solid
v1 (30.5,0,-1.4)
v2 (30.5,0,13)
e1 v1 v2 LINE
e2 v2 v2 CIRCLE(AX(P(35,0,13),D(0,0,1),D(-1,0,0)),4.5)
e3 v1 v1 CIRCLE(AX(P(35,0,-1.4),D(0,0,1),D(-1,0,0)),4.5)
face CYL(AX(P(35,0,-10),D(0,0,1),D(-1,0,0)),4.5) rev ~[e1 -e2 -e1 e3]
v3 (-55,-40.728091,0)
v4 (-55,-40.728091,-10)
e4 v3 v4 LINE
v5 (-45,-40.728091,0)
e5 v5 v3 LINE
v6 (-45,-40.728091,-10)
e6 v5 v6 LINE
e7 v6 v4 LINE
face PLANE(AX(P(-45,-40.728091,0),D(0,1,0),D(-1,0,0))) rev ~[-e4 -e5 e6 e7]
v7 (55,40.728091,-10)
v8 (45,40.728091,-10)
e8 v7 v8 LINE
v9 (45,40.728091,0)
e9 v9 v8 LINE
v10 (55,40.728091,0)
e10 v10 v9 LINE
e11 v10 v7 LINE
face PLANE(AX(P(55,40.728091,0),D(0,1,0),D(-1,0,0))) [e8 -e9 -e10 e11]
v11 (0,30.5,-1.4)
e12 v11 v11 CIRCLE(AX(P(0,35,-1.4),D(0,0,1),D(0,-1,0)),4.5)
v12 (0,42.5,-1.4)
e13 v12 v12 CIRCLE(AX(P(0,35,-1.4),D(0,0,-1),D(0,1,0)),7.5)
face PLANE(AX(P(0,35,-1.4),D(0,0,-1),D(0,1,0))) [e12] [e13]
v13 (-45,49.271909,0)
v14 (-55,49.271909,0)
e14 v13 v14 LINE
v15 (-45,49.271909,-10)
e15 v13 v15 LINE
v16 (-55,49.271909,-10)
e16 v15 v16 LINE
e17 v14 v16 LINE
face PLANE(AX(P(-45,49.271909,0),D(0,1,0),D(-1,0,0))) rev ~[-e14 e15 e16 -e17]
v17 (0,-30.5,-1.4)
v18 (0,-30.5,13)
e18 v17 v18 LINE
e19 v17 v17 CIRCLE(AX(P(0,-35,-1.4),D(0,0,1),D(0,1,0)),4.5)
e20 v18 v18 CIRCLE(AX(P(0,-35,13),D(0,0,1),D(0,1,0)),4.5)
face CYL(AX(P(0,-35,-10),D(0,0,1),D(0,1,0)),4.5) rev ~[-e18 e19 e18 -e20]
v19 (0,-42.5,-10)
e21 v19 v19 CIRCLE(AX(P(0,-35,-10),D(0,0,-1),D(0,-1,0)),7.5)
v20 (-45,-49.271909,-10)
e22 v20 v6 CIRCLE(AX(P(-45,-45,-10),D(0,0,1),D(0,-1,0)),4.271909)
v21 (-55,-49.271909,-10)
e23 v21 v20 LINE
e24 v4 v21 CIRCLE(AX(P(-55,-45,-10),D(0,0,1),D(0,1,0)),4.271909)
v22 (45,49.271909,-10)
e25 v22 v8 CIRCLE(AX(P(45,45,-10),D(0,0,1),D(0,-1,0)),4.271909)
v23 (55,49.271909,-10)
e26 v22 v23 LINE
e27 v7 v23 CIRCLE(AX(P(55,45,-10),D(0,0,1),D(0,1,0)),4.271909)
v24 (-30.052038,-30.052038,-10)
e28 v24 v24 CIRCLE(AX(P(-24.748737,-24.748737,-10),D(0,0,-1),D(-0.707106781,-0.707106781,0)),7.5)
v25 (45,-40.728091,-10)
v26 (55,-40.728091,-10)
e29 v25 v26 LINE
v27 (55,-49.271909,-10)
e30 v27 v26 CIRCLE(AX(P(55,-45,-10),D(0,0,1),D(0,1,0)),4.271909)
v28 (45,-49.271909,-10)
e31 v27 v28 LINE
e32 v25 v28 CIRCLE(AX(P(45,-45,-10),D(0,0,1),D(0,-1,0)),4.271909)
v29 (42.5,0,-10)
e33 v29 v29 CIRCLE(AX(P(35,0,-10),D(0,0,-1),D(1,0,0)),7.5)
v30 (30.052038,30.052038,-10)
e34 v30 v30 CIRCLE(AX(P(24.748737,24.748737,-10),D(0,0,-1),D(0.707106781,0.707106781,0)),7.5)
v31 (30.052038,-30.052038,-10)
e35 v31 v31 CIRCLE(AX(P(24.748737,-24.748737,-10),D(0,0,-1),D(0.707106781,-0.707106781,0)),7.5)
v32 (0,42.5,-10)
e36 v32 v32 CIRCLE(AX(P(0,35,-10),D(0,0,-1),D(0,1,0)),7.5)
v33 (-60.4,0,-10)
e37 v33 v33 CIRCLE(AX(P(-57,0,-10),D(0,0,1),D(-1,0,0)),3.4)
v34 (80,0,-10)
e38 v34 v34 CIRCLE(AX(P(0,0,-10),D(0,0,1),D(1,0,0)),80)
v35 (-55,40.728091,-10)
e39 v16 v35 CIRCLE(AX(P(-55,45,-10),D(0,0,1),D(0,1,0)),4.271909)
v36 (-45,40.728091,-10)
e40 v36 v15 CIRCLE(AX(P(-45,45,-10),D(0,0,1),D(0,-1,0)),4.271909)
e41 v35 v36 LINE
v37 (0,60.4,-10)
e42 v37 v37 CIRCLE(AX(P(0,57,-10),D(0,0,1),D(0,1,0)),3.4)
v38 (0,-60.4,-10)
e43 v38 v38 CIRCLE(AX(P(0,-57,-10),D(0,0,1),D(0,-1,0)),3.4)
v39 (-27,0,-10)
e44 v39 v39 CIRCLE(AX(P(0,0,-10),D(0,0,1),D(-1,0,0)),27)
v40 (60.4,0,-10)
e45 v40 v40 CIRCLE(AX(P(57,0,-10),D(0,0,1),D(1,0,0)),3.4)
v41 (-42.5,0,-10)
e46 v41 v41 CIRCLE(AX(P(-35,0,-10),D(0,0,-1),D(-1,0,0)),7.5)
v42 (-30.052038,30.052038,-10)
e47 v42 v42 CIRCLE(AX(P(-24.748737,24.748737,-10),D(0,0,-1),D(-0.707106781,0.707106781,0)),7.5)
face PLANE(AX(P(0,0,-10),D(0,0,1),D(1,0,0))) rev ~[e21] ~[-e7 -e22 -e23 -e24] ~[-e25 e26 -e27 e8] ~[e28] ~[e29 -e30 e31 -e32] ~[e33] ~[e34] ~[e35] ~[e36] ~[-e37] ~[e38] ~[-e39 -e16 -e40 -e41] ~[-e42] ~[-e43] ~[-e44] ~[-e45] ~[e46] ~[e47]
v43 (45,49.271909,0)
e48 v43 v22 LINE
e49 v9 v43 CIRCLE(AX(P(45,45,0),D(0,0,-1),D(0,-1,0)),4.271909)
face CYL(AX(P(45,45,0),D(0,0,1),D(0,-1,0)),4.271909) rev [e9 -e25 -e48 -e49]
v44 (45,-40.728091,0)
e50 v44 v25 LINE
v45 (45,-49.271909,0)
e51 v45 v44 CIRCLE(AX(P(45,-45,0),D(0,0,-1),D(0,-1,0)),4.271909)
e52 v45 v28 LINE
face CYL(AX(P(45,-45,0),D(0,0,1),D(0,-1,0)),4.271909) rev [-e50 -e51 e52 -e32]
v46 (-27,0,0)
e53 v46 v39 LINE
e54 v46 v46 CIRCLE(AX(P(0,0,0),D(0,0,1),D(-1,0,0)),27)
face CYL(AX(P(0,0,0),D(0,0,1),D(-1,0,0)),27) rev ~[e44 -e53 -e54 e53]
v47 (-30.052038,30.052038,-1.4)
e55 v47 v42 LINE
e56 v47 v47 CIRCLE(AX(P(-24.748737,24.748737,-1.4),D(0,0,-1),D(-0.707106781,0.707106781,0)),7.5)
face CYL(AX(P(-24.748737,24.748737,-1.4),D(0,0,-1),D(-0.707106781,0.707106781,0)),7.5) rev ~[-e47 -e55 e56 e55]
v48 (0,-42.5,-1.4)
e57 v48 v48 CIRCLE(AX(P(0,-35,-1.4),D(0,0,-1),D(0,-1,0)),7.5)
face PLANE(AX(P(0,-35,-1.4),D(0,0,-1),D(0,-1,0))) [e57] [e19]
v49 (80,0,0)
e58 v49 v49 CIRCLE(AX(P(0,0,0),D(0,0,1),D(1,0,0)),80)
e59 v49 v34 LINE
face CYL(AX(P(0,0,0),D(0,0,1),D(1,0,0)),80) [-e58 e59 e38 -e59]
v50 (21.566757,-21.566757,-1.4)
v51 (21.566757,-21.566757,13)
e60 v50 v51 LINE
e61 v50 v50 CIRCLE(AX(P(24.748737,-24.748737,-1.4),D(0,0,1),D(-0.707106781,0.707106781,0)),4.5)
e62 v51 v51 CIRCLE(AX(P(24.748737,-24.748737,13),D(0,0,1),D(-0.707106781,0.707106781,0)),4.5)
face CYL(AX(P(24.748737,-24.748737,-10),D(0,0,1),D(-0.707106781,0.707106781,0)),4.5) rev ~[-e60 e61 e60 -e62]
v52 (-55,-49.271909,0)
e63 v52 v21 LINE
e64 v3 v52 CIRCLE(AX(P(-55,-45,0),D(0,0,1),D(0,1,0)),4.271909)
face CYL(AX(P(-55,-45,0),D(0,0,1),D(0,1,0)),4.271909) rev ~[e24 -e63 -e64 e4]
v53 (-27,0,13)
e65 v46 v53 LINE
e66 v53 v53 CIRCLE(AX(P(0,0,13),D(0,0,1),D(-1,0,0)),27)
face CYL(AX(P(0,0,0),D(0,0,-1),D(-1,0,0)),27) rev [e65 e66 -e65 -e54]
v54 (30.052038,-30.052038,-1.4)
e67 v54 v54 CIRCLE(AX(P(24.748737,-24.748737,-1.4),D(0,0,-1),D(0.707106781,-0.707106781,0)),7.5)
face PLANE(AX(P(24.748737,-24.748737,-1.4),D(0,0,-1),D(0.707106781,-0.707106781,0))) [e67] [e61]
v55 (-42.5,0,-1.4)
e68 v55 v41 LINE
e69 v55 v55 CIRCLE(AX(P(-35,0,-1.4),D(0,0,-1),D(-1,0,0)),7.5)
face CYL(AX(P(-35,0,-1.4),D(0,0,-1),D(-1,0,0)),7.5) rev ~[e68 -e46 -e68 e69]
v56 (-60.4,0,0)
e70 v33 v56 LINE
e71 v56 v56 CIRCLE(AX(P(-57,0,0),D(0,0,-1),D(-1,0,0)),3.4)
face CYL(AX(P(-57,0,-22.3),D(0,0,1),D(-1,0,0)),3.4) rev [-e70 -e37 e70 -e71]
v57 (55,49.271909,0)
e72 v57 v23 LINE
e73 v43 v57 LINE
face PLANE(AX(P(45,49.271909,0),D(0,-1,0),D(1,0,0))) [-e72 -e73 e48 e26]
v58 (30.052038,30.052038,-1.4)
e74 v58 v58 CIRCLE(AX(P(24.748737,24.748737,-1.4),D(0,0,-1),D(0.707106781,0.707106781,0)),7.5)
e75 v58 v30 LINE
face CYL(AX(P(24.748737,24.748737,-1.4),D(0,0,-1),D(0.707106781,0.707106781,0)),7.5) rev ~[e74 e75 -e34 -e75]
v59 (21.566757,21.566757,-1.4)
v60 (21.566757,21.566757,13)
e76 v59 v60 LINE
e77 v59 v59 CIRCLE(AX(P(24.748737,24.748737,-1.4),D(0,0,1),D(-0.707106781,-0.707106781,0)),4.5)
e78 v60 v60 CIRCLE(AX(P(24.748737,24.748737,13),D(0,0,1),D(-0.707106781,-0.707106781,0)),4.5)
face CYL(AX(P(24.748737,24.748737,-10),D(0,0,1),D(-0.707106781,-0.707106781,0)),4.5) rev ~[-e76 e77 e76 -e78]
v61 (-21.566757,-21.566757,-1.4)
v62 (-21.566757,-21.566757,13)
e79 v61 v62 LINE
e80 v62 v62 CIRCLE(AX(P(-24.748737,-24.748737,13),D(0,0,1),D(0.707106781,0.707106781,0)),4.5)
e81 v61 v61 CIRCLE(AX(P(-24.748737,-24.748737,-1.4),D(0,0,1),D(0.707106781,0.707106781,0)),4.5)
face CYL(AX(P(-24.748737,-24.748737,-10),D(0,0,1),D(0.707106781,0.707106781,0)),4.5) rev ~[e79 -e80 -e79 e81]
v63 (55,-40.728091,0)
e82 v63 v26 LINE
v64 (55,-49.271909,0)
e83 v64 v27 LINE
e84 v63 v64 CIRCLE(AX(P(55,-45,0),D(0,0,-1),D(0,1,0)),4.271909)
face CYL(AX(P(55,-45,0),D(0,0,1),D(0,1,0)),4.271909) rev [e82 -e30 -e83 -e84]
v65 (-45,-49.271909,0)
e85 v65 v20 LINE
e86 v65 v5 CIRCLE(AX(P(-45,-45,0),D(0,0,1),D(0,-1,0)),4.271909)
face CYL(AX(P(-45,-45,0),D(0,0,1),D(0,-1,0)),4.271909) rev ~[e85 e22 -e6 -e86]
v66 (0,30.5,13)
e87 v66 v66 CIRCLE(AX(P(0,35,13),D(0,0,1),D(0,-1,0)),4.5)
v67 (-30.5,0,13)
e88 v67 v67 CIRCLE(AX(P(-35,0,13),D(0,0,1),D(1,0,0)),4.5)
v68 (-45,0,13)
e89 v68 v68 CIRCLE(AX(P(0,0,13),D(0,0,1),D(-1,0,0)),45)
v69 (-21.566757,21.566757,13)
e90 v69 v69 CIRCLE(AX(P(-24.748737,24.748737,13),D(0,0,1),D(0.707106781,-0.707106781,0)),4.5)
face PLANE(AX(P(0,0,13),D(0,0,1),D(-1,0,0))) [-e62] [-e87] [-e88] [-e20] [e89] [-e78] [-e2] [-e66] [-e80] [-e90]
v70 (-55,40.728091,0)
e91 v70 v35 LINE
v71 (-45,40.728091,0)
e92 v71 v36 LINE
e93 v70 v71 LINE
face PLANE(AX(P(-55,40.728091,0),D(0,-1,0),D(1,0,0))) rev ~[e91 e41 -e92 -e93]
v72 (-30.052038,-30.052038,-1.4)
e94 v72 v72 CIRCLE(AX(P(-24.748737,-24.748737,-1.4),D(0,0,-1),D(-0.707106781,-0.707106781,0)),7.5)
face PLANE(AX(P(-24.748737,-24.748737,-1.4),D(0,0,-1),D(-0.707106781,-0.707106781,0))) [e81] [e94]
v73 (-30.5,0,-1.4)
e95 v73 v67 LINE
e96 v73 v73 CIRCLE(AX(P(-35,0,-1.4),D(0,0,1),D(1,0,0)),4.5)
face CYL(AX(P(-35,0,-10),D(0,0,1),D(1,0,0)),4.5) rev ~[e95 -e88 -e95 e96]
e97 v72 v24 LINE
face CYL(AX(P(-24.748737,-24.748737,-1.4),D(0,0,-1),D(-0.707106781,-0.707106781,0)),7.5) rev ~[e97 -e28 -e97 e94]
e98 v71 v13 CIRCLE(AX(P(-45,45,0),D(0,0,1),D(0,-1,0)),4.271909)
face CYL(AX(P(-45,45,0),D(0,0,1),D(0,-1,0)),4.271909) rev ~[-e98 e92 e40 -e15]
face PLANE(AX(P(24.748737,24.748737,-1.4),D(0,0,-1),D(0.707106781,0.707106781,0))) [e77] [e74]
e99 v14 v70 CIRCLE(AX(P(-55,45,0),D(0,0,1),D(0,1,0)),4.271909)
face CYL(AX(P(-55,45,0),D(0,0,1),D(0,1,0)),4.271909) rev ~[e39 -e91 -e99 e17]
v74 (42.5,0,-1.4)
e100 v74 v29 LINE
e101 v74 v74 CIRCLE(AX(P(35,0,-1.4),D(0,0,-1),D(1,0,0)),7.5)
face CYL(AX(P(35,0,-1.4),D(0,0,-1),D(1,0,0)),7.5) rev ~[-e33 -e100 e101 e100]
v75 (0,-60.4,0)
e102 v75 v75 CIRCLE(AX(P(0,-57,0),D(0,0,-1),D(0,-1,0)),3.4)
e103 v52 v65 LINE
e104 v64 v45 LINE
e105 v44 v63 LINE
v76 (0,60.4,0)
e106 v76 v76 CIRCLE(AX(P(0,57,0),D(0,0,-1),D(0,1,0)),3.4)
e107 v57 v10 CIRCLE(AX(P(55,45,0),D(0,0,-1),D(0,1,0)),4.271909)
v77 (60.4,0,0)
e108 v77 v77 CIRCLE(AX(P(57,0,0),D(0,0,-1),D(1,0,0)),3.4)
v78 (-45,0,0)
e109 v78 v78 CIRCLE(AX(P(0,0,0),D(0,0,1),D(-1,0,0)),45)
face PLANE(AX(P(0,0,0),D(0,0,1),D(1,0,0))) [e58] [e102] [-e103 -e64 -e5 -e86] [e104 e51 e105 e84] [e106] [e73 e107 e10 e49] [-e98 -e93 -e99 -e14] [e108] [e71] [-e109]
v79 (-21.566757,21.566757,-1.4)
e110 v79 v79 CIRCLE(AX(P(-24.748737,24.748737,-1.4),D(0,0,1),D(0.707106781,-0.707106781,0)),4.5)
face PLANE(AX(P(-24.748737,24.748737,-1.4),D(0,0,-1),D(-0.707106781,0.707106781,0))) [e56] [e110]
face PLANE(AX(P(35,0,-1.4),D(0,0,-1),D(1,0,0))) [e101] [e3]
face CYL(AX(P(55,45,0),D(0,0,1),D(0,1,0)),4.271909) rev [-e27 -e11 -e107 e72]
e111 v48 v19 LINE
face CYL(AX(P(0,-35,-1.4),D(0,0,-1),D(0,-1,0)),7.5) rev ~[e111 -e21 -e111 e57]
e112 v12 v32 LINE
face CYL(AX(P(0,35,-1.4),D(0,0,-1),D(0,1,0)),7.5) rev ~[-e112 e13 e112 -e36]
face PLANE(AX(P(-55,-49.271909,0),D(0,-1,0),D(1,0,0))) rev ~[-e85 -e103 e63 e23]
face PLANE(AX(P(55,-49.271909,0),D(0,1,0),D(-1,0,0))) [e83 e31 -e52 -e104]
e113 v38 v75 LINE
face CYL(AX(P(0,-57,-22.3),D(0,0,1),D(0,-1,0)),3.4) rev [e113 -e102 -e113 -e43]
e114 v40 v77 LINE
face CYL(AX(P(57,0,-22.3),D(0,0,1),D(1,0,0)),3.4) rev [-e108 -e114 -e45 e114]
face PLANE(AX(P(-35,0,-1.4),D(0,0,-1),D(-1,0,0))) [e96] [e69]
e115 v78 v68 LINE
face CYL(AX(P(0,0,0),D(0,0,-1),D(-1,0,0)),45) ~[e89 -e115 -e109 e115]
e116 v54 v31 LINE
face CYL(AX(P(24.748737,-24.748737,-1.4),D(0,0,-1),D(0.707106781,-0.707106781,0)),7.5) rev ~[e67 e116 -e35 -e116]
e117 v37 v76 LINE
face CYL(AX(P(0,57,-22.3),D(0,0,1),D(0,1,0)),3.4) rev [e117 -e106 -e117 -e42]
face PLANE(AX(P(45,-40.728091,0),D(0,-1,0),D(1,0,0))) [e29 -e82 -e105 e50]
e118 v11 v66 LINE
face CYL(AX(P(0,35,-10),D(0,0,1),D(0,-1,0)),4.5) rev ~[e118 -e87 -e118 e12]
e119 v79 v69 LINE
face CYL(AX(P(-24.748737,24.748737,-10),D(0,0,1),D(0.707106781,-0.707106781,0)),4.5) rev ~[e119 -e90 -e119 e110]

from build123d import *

# Parameters (mm, degrees)
SKETCH1_R                                           = 45
SKETCH1_R_2                                         = 27
BOSS_EXTRUDE1_DEPTH                                 = 13
SKETCH2_R                                           = 80
BOSS_EXTRUDE2_DEPTH                                 = 10
CUT_EXTRUDE1_DEPTH                                  = 114.881517377
CIRPATTERN1_COUNT                                   = 4
SKETCH6_R                                           = 27
CUT_EXTRUDE2_DEPTH                                  = 114.881517377
CBORE_FOR_M8_HEX_SOCKET_HEAD_CAP_SCREW1_D           = 9
CBORE_FOR_M8_HEX_SOCKET_HEAD_CAP_SCREW1_CBORE_D     = 15
CBORE_FOR_M8_HEX_SOCKET_HEAD_CAP_SCREW1_CBORE_DEPTH = 8.6
CIRPATTERN2_COUNT                                   = 8


with BuildPart() as part:
    # Sketch1 → Boss-Extrude1 (new body)
    with BuildSketch(Plane.XY):
        with Locations(Location((0, 0, 0), (0, 0, 180))):
            Circle(SKETCH1_R)
        with Locations(Location((0, 0, 0), (0, 0, 180))):
            Circle(SKETCH1_R_2, mode=Mode.SUBTRACT)
    extrude(amount=BOSS_EXTRUDE1_DEPTH)

    # Sketch2 → Boss-Extrude2 (add)
    with BuildSketch(Plane.XY):
        Circle(SKETCH2_R)
    extrude(amount=-BOSS_EXTRUDE2_DEPTH)

    # Sketch3 → M8 Tapped Hole1 (revolve, cut)
    with BuildSketch(Plane(origin=(0, -57, 0), x_dir=(0, -1, 0), z_dir=(1, 0, 0))):
        Polygon((0, 0), (0, 24.342926105), (3.4, 22.3), (3.4, 0), align=None)
    m8_tapped_hole1 = revolve(axis=Axis((0, -57, 6.35), (0, 0, -1)), mode=Mode.SUBTRACT)

    # Sketch5 → Cut-Extrude1 (cut, through all)
    with BuildSketch(Plane.XY):
        with BuildLine():
            Line((45, 49.271909465), (55, 49.271909465))
            ThreePointArc((55, 49.271909465), (59.271909465, 45), (55, 40.728090535))
            Line((55, 40.728090535), (45, 40.728090535))
            ThreePointArc((45, 40.728090535), (40.728090535, 45), (45, 49.271909465))
        make_face()
        with BuildLine():
            Line((45, -40.728090535), (55, -40.728090535))
            ThreePointArc((55, -40.728090535), (59.271909465, -45), (55, -49.271909465))
            Line((55, -49.271909465), (45, -49.271909465))
            ThreePointArc((45, -49.271909465), (40.728090535, -45), (45, -40.728090535))
        make_face()
        with BuildLine():
            Line((-45, -40.728090535), (-55, -40.728090535))
            ThreePointArc((-55, -40.728090535), (-59.271909465, -45), (-55, -49.271909465))
            Line((-55, -49.271909465), (-45, -49.271909465))
            ThreePointArc((-45, -49.271909465), (-40.728090535, -45), (-45, -40.728090535))
        make_face()
        with BuildLine():
            Line((-45, 49.271909465), (-55, 49.271909465))
            ThreePointArc((-55, 49.271909465), (-59.271909465, 45), (-55, 40.728090535))
            Line((-55, 40.728090535), (-45, 40.728090535))
            ThreePointArc((-45, 40.728090535), (-40.728090535, 45), (-45, 49.271909465))
        make_face()
    extrude(amount=-CUT_EXTRUDE1_DEPTH, mode=Mode.SUBTRACT)

    # CirPattern1: M8 Tapped Hole1 ×4 about axis
    cirpattern1_axis = Axis((0, 0, 0), (0, 0, 1))
    for i in range(1, CIRPATTERN1_COUNT):
        add(m8_tapped_hole1.rotate(cirpattern1_axis, i * 360 / CIRPATTERN1_COUNT), mode=Mode.SUBTRACT)

    # Sketch6 → Cut-Extrude2 (cut, through all)
    with BuildSketch(Plane.XY):
        with Locations(Location((0, 0, 0), (0, 0, 180))):
            Circle(SKETCH6_R)
    extrude(amount=-CUT_EXTRUDE2_DEPTH, mode=Mode.SUBTRACT)

    # CBORE for M8 Hex Socket Head Cap Screw1 (through all)
    with Locations(Plane(origin=(0, 0, -10), x_dir=(-1, 0, 0), z_dir=(0, 0, -1))):
        with Locations((35, 0)):
            cbore_for_m8_hex_socket_head_cap_screw1 = CounterBoreHole(CBORE_FOR_M8_HEX_SOCKET_HEAD_CAP_SCREW1_D / 2, CBORE_FOR_M8_HEX_SOCKET_HEAD_CAP_SCREW1_CBORE_D / 2, CBORE_FOR_M8_HEX_SOCKET_HEAD_CAP_SCREW1_CBORE_DEPTH)

    # CirPattern2: CBORE for M8 Hex Socket Head Cap Screw1 ×8 about axis
    cirpattern2_axis = Axis((0, 0, 0), (0, 0, 1))
    for i in range(1, CIRPATTERN2_COUNT):
        add(cbore_for_m8_hex_socket_head_cap_screw1.rotate(cirpattern2_axis, i * 360 / CIRPATTERN2_COUNT), mode=Mode.SUBTRACT)


solid = part.part
